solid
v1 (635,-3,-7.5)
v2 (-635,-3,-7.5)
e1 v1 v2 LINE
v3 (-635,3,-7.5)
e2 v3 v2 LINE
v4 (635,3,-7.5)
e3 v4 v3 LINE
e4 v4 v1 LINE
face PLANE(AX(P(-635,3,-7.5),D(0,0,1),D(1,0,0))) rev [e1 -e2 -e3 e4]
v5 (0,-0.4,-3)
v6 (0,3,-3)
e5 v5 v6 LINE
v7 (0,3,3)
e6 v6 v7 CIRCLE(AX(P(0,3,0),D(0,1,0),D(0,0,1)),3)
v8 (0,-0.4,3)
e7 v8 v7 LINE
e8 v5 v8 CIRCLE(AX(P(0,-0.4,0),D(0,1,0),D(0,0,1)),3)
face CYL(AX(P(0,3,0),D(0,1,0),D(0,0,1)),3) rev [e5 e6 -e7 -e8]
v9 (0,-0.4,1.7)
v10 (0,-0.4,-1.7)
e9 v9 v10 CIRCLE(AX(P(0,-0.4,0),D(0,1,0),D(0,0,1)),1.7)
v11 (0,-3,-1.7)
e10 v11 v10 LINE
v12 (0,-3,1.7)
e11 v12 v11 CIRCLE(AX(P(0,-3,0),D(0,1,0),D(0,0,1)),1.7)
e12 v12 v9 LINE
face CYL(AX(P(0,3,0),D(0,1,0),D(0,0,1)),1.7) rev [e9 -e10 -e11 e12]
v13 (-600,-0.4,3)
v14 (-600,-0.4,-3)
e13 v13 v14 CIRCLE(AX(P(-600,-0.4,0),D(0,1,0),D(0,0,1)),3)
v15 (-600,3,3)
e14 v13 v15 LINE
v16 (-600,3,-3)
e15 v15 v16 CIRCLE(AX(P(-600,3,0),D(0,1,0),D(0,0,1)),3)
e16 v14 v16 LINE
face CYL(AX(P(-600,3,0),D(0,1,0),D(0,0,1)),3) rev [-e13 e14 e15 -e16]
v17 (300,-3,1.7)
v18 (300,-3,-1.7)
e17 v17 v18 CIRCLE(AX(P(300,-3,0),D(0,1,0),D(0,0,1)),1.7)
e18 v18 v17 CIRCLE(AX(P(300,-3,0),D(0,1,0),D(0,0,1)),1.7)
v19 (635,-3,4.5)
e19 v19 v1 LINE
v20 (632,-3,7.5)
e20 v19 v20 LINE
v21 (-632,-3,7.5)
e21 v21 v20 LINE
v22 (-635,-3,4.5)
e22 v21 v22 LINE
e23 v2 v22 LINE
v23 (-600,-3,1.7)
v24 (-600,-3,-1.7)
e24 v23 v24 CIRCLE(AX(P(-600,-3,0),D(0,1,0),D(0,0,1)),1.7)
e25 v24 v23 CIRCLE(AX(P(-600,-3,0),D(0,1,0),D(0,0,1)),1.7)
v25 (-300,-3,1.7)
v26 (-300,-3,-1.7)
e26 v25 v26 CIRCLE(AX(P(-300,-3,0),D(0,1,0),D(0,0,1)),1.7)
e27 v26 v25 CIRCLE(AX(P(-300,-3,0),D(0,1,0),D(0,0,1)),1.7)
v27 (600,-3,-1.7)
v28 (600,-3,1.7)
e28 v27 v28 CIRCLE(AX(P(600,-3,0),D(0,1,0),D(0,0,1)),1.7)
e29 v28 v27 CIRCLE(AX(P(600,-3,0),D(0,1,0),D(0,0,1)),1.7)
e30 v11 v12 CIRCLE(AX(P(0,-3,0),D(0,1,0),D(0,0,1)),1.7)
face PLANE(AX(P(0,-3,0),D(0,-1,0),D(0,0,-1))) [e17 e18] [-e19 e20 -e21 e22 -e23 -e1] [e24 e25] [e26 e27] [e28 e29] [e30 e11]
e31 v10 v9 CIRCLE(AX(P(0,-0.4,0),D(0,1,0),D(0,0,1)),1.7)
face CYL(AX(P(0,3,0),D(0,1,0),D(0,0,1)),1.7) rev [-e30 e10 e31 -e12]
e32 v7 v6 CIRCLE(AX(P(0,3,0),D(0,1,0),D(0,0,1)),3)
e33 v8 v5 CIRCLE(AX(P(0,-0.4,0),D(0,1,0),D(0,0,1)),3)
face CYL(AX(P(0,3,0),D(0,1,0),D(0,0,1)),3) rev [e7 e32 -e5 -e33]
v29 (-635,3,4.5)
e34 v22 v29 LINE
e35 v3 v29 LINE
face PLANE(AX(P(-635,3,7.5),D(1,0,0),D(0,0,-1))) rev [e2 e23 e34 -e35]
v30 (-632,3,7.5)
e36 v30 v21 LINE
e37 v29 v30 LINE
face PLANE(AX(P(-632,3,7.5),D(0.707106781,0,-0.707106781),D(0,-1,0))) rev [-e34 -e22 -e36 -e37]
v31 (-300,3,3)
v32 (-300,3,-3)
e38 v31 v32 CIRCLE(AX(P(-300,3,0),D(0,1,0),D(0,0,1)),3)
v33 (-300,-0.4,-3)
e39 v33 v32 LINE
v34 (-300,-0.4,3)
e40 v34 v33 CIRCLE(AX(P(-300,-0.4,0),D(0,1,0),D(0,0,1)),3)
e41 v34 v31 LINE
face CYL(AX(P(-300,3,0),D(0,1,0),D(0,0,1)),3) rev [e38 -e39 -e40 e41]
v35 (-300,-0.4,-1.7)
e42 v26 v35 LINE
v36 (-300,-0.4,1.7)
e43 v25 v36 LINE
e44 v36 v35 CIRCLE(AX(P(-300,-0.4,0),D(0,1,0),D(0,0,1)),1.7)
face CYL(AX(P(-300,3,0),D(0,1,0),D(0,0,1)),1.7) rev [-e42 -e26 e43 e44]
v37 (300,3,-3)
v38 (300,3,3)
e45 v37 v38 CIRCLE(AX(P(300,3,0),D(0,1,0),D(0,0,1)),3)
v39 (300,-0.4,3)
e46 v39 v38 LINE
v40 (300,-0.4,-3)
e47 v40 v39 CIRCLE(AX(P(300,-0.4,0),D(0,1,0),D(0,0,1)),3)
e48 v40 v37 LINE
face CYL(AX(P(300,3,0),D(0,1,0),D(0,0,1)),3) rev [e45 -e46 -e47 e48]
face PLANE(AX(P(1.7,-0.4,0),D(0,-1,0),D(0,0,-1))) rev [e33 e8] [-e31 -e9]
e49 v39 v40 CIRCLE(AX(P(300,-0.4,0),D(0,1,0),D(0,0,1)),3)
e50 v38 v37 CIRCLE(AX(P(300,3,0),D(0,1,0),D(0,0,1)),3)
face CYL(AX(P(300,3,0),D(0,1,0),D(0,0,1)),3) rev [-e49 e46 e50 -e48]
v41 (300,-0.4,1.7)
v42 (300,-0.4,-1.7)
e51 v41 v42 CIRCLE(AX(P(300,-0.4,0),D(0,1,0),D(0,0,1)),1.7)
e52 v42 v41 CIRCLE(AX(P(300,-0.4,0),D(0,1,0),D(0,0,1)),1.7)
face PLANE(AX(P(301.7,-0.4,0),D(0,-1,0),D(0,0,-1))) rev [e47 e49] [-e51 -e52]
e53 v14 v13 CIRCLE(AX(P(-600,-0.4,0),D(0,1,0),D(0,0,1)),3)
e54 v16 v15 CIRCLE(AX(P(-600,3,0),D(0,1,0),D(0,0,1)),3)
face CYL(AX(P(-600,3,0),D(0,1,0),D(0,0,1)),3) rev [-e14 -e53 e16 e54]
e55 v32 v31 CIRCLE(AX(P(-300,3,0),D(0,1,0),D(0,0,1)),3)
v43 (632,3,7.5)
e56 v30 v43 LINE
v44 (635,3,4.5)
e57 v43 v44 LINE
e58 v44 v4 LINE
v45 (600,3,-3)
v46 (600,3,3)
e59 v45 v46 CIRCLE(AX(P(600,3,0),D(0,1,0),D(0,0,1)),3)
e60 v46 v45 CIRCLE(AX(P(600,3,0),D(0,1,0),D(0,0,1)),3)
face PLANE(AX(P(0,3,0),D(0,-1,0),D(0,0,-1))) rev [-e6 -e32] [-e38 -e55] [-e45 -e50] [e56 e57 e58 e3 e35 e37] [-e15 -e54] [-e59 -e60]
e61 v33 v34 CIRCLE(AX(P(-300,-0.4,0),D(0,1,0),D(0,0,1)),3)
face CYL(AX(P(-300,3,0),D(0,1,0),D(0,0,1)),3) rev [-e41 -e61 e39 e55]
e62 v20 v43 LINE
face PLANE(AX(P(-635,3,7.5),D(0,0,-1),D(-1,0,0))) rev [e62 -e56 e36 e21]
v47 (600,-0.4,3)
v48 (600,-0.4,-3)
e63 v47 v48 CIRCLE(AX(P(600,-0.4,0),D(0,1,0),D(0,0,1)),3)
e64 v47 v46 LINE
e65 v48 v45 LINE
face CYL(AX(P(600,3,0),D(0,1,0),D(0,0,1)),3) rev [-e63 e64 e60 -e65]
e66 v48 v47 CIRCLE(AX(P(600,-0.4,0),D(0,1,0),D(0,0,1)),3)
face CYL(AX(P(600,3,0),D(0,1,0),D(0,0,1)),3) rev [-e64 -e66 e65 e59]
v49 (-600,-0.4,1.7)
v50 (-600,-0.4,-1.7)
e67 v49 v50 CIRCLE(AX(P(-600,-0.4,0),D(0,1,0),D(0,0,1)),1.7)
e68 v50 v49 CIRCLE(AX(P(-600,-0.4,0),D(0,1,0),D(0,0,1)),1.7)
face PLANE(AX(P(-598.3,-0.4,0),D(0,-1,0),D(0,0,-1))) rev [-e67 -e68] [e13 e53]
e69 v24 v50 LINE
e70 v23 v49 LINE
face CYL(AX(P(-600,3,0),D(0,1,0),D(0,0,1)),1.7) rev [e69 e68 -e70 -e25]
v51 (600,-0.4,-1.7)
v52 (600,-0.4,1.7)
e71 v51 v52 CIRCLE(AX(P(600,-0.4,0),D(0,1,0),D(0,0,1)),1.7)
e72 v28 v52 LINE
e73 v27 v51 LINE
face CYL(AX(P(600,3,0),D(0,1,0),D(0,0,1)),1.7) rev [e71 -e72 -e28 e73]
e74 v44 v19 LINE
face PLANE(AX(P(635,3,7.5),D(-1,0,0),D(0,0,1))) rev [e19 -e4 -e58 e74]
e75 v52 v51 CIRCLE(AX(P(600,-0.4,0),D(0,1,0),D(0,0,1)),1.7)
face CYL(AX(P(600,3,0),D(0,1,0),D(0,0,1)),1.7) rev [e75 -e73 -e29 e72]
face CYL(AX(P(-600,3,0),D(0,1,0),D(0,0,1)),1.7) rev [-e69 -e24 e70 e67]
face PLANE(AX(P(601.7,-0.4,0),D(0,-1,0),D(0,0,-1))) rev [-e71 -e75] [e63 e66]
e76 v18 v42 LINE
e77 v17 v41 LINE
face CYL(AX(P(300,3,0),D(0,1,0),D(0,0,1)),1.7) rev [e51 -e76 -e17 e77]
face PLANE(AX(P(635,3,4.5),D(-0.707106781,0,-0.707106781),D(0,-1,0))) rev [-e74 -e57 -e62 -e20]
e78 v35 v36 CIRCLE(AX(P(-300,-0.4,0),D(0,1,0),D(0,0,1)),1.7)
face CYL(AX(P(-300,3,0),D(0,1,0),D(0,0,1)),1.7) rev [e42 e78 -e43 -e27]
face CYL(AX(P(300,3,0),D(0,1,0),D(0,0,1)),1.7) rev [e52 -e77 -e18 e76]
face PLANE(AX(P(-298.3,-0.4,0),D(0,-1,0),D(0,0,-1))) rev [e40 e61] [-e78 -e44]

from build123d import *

# Parameters (mm, degrees)
SKETCH_1_W                = 1270
SKETCH_1_H                = 15
EXTRUDE_1_DEPTH           = 3
CHAMFER_1_SIZE            = 3
HOLE_WIZARD_1_D           = 3.4
HOLE_WIZARD_1_CBORE_D     = 6
HOLE_WIZARD_1_CBORE_DEPTH = 3.4


with BuildPart() as part:
    # 草图1 → 凸台-拉伸1 (new, symmetric)
    with BuildSketch(Plane(origin=(0, 0, 0), x_dir=(1, 0, 0), z_dir=(0, 1, 0))):
        Rectangle(SKETCH_1_W, SKETCH_1_H)
    extrude(amount=EXTRUDE_1_DEPTH, both=True)

    # 倒角1
    chamfer_1_edges = [part.edges().sort_by_distance(p)[0] for p in [
        (635, 0, 7.5),
        (-635, 0, 7.5),
    ]]
    chamfer(chamfer_1_edges, length=CHAMFER_1_SIZE)

    # 打孔尺寸(%根据)内六角圆柱头螺钉的类型1 (through all)
    with Locations(Plane(origin=(0, 3, 0), x_dir=(1, 0, 0), z_dir=(0, 1, 0))):
        with Locations((-600, 0), (-300, 0), (0, 0), (300, 0), (600, 0)):
            CounterBoreHole(HOLE_WIZARD_1_D / 2, HOLE_WIZARD_1_CBORE_D / 2, HOLE_WIZARD_1_CBORE_DEPTH)


solid = part.part
